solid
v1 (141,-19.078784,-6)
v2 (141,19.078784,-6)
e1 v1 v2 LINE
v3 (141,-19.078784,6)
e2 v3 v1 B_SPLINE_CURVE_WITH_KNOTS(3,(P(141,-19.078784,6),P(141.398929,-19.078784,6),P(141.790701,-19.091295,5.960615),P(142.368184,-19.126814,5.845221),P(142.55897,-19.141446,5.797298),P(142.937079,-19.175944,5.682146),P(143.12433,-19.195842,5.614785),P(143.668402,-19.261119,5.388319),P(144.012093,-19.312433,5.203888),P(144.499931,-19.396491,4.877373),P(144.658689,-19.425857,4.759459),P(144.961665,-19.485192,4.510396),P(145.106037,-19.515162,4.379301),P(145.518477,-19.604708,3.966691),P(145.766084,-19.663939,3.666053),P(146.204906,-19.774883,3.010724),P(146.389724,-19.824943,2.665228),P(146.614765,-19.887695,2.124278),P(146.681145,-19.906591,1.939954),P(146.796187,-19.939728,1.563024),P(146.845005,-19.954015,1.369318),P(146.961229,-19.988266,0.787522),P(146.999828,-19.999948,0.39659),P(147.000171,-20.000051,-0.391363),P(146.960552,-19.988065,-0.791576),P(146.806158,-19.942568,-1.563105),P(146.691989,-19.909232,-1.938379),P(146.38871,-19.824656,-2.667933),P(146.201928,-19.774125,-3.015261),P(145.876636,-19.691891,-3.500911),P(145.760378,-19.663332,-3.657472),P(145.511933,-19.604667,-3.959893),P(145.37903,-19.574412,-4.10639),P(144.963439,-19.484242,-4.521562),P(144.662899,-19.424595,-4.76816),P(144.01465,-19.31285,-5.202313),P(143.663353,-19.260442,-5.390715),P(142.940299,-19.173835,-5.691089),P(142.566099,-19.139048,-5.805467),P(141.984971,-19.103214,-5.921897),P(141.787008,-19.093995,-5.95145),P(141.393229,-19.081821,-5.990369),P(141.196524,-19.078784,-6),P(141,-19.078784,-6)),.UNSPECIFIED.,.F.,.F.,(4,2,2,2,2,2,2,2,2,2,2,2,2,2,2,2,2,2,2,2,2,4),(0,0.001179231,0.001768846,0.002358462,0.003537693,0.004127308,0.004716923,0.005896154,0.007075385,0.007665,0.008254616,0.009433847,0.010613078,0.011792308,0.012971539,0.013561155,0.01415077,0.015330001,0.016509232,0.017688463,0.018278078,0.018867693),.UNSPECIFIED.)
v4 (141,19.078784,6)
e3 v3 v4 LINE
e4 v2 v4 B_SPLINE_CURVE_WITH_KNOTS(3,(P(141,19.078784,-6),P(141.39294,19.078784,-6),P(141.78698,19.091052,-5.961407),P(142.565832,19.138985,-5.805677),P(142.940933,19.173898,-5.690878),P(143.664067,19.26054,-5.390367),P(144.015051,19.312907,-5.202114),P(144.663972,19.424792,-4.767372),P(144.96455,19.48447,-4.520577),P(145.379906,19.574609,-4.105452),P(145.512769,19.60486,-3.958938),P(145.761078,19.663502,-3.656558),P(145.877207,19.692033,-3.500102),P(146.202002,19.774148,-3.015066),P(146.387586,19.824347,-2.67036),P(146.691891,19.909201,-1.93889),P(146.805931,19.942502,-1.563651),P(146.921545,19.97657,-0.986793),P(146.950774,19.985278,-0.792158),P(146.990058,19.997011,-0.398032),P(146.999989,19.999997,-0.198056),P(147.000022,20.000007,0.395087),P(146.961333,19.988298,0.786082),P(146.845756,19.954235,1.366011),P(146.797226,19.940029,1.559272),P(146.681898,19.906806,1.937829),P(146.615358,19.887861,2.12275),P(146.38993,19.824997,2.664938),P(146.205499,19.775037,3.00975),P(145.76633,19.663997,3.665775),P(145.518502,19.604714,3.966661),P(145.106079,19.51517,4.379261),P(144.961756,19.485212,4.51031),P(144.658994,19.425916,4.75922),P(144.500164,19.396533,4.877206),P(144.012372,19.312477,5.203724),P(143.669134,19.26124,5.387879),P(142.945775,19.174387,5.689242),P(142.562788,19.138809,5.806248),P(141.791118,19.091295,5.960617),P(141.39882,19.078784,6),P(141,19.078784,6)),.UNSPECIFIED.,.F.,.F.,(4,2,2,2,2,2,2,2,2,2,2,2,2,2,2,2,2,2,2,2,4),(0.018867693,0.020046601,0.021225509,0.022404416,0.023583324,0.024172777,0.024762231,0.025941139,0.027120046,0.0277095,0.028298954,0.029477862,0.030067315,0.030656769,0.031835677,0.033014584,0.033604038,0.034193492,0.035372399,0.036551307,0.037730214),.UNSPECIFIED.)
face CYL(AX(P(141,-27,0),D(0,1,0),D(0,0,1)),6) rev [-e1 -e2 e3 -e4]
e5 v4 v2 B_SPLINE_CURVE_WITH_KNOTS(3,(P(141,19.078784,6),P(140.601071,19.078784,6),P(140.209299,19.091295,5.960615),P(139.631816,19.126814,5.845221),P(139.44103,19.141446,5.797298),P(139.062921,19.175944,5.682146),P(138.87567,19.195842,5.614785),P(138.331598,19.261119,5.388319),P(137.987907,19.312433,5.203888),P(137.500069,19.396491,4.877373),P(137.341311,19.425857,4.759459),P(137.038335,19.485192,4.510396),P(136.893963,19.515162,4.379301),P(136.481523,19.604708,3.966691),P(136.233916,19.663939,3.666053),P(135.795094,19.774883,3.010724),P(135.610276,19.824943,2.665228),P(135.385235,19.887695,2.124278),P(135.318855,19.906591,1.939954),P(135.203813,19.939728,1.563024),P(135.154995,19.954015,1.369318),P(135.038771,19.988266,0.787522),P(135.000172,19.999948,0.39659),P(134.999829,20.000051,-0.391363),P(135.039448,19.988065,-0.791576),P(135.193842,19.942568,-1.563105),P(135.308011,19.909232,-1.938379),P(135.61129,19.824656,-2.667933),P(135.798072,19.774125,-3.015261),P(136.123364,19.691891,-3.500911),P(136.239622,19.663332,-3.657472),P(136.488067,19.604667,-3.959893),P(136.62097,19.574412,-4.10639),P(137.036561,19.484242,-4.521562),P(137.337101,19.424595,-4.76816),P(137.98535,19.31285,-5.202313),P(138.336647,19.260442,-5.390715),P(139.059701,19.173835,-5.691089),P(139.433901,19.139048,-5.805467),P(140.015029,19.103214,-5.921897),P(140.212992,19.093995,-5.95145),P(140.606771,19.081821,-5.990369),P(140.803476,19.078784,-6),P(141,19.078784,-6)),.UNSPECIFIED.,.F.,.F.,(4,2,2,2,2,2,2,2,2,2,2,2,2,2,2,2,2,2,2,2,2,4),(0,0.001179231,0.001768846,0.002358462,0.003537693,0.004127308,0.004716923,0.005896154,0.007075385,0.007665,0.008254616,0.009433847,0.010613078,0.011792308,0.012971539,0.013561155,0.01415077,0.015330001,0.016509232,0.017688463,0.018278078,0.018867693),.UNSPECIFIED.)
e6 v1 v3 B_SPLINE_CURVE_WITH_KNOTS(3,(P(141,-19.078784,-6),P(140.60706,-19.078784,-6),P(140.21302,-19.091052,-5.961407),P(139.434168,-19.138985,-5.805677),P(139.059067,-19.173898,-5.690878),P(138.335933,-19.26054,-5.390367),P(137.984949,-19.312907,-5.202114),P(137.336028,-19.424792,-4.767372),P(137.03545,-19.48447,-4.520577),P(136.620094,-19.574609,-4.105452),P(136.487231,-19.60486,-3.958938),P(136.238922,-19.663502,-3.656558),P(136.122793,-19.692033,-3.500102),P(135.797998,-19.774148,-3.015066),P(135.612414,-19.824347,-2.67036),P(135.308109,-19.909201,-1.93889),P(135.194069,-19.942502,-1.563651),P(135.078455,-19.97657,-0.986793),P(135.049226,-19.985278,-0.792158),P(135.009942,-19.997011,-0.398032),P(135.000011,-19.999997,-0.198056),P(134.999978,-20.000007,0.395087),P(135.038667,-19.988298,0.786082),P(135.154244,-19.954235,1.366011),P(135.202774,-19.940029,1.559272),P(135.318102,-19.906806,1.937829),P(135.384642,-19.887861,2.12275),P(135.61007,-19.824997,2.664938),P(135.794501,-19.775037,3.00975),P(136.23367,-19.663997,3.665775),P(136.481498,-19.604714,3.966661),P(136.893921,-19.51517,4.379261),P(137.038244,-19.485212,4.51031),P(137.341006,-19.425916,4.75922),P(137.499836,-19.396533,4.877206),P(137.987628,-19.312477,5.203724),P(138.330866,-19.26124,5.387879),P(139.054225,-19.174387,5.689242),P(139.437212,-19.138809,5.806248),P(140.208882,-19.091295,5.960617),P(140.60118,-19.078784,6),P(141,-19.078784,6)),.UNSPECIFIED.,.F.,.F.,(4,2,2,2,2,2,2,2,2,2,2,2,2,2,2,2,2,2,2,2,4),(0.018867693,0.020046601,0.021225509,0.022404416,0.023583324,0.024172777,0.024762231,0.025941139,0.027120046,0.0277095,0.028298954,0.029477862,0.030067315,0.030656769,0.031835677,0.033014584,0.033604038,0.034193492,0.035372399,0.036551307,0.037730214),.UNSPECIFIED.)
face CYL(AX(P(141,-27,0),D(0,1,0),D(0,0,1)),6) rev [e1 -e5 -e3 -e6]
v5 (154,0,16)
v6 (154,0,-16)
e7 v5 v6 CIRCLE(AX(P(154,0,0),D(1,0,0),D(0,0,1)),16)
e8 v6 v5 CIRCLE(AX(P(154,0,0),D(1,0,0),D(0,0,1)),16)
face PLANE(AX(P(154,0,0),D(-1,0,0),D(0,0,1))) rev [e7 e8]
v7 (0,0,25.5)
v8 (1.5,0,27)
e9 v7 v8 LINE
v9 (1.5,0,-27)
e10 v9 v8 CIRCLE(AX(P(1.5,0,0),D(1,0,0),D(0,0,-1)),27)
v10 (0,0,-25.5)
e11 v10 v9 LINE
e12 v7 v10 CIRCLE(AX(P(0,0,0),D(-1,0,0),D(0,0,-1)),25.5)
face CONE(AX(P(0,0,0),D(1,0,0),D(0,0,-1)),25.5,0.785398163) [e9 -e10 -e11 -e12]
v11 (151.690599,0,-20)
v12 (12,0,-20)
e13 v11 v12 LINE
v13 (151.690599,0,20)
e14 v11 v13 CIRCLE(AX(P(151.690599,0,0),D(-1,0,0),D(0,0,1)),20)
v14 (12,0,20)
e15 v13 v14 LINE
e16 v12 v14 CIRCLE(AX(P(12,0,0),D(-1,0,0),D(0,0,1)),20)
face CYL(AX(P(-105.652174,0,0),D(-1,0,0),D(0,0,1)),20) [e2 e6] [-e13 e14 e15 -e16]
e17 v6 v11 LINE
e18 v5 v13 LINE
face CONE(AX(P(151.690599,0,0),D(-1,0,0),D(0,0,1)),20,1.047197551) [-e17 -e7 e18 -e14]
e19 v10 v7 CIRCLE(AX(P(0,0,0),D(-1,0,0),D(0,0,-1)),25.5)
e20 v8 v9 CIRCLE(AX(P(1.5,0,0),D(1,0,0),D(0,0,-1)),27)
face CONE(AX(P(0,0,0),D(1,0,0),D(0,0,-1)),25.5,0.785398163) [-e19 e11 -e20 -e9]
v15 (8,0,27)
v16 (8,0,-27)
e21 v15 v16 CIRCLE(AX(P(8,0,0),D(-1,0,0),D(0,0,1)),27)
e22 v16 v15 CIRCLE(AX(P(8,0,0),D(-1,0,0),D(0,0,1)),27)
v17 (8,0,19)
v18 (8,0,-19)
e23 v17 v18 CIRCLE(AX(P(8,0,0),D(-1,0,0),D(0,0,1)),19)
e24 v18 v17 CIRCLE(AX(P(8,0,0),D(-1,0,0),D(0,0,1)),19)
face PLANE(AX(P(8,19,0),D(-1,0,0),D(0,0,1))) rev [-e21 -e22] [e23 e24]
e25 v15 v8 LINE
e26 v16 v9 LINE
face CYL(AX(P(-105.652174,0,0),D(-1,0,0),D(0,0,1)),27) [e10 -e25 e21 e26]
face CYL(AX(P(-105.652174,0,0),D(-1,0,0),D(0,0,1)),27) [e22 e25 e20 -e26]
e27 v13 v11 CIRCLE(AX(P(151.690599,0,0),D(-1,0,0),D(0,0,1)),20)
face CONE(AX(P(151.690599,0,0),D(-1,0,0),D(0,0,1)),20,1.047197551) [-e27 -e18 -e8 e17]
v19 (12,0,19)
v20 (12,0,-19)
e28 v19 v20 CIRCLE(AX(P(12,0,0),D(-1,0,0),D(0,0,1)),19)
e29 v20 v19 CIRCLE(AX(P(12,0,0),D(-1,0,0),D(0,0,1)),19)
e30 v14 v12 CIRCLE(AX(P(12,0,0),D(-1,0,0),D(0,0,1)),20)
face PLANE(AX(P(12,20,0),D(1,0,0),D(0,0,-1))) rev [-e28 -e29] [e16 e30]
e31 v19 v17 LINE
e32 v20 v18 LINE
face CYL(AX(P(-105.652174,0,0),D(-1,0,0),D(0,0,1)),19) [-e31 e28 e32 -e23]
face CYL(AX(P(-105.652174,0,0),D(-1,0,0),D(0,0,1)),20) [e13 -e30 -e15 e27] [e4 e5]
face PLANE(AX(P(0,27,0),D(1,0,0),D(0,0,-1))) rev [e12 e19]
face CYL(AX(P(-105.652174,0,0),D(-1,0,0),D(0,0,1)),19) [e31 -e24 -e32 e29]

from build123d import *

# Parameters (mm, degrees)
CHAMFER_1_SIZE           = 1.5
CHAMFER_2_SIZE           = 4
CHAMFER_2_SIZE2          = 2.309401077
CUT_EXTRUDE_1_DEPTH      = 159.663165227
CUT_EXTRUDE_1_DEPTH_BACK = 159.663165227
SKETCH_2_R               = 6


with BuildPart() as part:
    # 草图1 → 旋转1 (revolve)
    with BuildSketch(Plane.XY, mode=Mode.PRIVATE) as revolve_1_sk:
        Polygon((0, 0), (154, 0), (154, 20), (12, 20), (12, 19), (8, 19), (8, 27), (0, 27), align=None)
    revolve(revolve_1_sk.sketch.rotate(Axis((-105.652173913, 0, 0), (1, 0, 0)), 90), axis=Axis((-105.652173913, 0, 0), (1, 0, 0)))

    # 倒角1
    chamfer_1_edges = [part.edges().sort_by_distance(p)[0] for p in [
        (0, 0, -27),
    ]]
    chamfer(chamfer_1_edges, length=CHAMFER_1_SIZE)

    # 倒角2
    chamfer_2_edges = [part.edges().sort_by_distance(p)[0] for p in [
        (154, 0, -20),
    ]]
    chamfer_2_side = [part.faces().sort_by_distance(p)[0] for p in [
        (154, 0, 0),
    ]]
    chamfer(chamfer_2_edges, length=CHAMFER_2_SIZE, length2=CHAMFER_2_SIZE2, reference=chamfer_2_side[0])

    # 草图2 → 切除-拉伸1 (cut, two sides: drawn at the far end of the back side and taken through both)
    with BuildSketch(Plane(origin=(0, 0, 0), x_dir=(1, 0, 0), z_dir=(0, 1, 0)).offset(-CUT_EXTRUDE_1_DEPTH_BACK)):
        with Locations(Location((141, 0, 0), (0, 0, 270))):
            Circle(SKETCH_2_R)
    extrude(amount=CUT_EXTRUDE_1_DEPTH + CUT_EXTRUDE_1_DEPTH_BACK, mode=Mode.SUBTRACT)


solid = part.part
